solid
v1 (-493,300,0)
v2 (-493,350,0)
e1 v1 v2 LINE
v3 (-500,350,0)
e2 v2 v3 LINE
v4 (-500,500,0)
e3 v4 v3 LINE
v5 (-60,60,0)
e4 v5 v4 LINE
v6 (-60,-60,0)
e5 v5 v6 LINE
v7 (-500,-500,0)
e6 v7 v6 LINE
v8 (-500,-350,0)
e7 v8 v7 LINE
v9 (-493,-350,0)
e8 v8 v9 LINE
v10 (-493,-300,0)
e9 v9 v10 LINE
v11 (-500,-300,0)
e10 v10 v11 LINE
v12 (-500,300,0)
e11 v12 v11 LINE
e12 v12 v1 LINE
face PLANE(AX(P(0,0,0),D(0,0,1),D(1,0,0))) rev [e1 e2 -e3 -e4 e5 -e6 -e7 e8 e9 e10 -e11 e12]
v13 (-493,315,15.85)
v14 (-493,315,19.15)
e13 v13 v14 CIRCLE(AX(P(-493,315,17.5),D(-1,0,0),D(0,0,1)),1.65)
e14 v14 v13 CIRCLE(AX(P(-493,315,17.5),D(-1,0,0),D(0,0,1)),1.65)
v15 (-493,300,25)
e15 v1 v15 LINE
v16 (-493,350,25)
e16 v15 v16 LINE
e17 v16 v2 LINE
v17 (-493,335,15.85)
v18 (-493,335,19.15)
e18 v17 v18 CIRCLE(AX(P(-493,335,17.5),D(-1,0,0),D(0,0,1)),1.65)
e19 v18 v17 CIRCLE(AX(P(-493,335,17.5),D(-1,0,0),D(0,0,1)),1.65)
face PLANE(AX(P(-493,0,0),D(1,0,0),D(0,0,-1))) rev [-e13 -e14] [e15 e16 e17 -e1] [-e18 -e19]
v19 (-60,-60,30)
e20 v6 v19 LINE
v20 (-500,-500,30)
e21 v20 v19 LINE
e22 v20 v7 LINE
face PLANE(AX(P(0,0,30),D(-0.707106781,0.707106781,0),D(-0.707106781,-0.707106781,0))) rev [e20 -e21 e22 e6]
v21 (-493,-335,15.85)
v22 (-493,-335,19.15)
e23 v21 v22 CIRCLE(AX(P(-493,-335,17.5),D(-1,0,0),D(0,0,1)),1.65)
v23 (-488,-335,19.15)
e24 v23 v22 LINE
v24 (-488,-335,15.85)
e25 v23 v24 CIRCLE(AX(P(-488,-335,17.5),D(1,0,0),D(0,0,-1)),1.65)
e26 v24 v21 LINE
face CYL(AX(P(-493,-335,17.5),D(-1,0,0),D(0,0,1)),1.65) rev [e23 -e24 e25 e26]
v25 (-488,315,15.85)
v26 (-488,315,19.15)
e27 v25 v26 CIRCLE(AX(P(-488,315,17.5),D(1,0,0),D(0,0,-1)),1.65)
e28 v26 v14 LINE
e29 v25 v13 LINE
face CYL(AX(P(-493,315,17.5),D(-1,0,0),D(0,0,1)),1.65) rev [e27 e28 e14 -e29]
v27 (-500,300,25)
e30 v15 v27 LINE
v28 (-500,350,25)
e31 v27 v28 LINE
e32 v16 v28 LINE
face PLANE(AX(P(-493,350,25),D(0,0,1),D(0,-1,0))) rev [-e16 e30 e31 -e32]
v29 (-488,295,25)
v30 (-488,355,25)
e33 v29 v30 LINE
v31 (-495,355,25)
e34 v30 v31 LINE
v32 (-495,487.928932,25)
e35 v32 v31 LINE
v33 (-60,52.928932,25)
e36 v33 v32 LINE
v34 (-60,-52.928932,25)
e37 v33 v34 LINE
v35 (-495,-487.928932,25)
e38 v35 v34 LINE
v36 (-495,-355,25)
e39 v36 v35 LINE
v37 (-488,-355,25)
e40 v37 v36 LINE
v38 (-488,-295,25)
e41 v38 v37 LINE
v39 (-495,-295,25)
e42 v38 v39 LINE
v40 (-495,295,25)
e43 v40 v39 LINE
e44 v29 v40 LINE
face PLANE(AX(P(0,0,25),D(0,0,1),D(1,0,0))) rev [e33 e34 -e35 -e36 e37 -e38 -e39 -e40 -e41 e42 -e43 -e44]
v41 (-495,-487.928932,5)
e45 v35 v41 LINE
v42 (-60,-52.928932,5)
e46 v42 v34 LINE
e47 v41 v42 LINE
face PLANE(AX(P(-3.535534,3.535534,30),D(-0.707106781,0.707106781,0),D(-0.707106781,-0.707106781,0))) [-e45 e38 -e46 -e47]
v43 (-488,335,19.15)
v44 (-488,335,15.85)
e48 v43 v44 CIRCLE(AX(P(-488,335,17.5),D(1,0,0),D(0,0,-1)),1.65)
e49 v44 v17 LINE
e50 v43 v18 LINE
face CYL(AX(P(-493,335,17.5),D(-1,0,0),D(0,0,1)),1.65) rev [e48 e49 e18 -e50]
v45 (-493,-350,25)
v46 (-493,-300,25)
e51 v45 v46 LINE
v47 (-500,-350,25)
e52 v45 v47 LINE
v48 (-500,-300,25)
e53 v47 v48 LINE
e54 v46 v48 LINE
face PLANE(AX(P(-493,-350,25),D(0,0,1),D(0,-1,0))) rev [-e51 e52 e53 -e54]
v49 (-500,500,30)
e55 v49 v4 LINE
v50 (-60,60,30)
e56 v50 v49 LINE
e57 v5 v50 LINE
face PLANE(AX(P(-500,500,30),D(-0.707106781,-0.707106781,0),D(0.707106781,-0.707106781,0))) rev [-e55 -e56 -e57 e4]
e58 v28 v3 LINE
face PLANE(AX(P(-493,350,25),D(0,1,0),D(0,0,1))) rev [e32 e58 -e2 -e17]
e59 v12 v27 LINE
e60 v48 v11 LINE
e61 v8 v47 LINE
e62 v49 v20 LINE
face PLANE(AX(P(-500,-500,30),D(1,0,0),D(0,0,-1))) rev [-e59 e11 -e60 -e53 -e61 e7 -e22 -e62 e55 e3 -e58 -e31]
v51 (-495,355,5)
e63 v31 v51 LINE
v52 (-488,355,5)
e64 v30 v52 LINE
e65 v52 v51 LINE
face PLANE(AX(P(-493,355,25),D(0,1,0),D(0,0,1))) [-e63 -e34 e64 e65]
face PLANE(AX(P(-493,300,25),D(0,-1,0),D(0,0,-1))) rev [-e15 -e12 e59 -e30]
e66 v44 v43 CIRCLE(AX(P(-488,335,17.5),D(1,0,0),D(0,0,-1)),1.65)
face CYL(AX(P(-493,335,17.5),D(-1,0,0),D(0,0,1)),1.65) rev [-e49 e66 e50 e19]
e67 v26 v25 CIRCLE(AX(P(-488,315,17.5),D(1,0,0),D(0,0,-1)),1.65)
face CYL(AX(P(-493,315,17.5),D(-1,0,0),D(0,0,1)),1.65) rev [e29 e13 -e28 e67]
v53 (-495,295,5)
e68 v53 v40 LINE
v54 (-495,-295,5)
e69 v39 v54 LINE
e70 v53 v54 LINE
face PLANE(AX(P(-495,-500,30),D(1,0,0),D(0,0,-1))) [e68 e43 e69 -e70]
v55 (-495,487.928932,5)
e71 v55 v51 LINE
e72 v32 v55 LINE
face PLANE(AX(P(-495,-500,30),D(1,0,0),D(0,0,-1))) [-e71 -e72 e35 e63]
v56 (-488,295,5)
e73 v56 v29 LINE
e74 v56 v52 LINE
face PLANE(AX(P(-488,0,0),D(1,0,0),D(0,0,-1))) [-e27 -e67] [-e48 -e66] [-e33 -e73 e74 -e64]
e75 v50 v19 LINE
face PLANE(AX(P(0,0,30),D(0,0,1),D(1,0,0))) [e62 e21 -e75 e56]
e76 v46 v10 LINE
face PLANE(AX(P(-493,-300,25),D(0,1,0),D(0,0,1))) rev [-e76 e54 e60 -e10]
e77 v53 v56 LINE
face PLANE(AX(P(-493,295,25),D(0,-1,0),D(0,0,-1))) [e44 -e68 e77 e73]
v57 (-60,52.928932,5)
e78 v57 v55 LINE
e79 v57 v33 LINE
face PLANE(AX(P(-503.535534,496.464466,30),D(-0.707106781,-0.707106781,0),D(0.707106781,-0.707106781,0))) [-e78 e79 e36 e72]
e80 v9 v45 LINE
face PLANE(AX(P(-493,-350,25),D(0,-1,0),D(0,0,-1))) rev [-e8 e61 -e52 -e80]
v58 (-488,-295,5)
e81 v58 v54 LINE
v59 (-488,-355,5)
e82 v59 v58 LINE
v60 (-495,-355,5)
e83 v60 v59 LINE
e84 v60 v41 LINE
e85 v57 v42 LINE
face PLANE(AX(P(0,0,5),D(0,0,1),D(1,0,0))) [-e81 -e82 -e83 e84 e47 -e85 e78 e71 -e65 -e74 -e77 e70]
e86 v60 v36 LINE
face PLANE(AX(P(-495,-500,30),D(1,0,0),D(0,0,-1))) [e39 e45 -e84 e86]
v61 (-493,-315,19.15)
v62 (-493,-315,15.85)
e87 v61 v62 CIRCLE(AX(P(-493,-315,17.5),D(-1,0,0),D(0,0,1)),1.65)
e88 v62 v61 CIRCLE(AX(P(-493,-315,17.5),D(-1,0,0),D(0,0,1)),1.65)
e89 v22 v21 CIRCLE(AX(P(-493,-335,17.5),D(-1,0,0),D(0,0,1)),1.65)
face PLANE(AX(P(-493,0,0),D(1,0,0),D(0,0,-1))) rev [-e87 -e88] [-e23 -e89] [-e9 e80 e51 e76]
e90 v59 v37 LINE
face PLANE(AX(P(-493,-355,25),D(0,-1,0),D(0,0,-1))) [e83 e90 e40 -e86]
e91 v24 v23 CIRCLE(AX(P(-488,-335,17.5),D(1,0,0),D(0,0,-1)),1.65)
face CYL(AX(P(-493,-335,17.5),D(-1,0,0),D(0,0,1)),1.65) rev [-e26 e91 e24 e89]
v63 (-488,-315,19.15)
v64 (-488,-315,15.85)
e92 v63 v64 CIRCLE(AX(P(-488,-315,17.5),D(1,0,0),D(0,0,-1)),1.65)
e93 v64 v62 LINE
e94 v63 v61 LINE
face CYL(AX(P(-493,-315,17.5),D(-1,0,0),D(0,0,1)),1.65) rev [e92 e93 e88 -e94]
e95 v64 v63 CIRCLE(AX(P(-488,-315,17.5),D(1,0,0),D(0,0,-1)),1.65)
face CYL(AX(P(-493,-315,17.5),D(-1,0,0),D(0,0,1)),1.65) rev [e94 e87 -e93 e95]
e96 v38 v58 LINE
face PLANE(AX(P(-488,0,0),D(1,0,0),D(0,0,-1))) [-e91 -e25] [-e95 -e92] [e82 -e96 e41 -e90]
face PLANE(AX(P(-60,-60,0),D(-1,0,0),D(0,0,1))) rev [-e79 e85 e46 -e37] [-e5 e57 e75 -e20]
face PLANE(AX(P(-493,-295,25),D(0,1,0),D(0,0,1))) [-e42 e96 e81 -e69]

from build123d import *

# Parameters (mm, degrees)
BOSS_EXTRUDE1_DEPTH   = 30
SKETCH2_W             = 120
SKETCH2_H             = 120
CUT_EXTRUDE1_DEPTH    = 30
SKETCH3_W             = 90
SKETCH3_H             = 50
CUT_EXTRUDE2_DEPTH    = 7
SHELL1_T              = -5
M4_TAPPED_HOLE1_D     = 3.3
M4_TAPPED_HOLE1_DEPTH = 10.1
M4_TAPPED_HOLE1_TIP   = 0.991420021


with BuildPart() as part:
    # Sketch1 → Boss-Extrude1 (new body)
    with BuildSketch(Plane.XY):
        Polygon((-500, 500), (0, 0), (-500, -500), align=None)
    extrude(amount=BOSS_EXTRUDE1_DEPTH)

    # Sketch2 → Cut-Extrude1 (cut)
    with BuildSketch(Plane.XY.offset(30)):
        Rectangle(SKETCH2_W, SKETCH2_H)
    extrude(amount=-CUT_EXTRUDE1_DEPTH, mode=Mode.SUBTRACT)

    # Sketch3 → Cut-Extrude2 (cut)
    with BuildSketch(Plane.ZY.offset(500)):
        with Locations((-20, 325)):
            Rectangle(SKETCH3_W, SKETCH3_H)
        with Locations((-20, -325)):
            Rectangle(SKETCH3_W, SKETCH3_H)
    extrude(amount=-CUT_EXTRUDE2_DEPTH, mode=Mode.SUBTRACT)

    # Shell1
    shell1_openings = [part.faces().sort_by_distance(p)[0] for p in [
        (-60, 0, 15),
    ]]
    offset(amount=SHELL1_T, openings=shell1_openings, kind=Kind.INTERSECTION)

    # M4 Tapped Hole1
    with Locations(Plane.ZY.offset(493)):
        with Locations((17.5, 335), (17.5, 315), (17.5, -315), (17.5, -335)):
            Hole(M4_TAPPED_HOLE1_D / 2, depth=M4_TAPPED_HOLE1_DEPTH)
            with Locations((0, 0, -(M4_TAPPED_HOLE1_DEPTH + M4_TAPPED_HOLE1_TIP / 2))):  # 118° drill point
                Cone(0, M4_TAPPED_HOLE1_D / 2, M4_TAPPED_HOLE1_TIP, mode=Mode.SUBTRACT)


solid = part.part
